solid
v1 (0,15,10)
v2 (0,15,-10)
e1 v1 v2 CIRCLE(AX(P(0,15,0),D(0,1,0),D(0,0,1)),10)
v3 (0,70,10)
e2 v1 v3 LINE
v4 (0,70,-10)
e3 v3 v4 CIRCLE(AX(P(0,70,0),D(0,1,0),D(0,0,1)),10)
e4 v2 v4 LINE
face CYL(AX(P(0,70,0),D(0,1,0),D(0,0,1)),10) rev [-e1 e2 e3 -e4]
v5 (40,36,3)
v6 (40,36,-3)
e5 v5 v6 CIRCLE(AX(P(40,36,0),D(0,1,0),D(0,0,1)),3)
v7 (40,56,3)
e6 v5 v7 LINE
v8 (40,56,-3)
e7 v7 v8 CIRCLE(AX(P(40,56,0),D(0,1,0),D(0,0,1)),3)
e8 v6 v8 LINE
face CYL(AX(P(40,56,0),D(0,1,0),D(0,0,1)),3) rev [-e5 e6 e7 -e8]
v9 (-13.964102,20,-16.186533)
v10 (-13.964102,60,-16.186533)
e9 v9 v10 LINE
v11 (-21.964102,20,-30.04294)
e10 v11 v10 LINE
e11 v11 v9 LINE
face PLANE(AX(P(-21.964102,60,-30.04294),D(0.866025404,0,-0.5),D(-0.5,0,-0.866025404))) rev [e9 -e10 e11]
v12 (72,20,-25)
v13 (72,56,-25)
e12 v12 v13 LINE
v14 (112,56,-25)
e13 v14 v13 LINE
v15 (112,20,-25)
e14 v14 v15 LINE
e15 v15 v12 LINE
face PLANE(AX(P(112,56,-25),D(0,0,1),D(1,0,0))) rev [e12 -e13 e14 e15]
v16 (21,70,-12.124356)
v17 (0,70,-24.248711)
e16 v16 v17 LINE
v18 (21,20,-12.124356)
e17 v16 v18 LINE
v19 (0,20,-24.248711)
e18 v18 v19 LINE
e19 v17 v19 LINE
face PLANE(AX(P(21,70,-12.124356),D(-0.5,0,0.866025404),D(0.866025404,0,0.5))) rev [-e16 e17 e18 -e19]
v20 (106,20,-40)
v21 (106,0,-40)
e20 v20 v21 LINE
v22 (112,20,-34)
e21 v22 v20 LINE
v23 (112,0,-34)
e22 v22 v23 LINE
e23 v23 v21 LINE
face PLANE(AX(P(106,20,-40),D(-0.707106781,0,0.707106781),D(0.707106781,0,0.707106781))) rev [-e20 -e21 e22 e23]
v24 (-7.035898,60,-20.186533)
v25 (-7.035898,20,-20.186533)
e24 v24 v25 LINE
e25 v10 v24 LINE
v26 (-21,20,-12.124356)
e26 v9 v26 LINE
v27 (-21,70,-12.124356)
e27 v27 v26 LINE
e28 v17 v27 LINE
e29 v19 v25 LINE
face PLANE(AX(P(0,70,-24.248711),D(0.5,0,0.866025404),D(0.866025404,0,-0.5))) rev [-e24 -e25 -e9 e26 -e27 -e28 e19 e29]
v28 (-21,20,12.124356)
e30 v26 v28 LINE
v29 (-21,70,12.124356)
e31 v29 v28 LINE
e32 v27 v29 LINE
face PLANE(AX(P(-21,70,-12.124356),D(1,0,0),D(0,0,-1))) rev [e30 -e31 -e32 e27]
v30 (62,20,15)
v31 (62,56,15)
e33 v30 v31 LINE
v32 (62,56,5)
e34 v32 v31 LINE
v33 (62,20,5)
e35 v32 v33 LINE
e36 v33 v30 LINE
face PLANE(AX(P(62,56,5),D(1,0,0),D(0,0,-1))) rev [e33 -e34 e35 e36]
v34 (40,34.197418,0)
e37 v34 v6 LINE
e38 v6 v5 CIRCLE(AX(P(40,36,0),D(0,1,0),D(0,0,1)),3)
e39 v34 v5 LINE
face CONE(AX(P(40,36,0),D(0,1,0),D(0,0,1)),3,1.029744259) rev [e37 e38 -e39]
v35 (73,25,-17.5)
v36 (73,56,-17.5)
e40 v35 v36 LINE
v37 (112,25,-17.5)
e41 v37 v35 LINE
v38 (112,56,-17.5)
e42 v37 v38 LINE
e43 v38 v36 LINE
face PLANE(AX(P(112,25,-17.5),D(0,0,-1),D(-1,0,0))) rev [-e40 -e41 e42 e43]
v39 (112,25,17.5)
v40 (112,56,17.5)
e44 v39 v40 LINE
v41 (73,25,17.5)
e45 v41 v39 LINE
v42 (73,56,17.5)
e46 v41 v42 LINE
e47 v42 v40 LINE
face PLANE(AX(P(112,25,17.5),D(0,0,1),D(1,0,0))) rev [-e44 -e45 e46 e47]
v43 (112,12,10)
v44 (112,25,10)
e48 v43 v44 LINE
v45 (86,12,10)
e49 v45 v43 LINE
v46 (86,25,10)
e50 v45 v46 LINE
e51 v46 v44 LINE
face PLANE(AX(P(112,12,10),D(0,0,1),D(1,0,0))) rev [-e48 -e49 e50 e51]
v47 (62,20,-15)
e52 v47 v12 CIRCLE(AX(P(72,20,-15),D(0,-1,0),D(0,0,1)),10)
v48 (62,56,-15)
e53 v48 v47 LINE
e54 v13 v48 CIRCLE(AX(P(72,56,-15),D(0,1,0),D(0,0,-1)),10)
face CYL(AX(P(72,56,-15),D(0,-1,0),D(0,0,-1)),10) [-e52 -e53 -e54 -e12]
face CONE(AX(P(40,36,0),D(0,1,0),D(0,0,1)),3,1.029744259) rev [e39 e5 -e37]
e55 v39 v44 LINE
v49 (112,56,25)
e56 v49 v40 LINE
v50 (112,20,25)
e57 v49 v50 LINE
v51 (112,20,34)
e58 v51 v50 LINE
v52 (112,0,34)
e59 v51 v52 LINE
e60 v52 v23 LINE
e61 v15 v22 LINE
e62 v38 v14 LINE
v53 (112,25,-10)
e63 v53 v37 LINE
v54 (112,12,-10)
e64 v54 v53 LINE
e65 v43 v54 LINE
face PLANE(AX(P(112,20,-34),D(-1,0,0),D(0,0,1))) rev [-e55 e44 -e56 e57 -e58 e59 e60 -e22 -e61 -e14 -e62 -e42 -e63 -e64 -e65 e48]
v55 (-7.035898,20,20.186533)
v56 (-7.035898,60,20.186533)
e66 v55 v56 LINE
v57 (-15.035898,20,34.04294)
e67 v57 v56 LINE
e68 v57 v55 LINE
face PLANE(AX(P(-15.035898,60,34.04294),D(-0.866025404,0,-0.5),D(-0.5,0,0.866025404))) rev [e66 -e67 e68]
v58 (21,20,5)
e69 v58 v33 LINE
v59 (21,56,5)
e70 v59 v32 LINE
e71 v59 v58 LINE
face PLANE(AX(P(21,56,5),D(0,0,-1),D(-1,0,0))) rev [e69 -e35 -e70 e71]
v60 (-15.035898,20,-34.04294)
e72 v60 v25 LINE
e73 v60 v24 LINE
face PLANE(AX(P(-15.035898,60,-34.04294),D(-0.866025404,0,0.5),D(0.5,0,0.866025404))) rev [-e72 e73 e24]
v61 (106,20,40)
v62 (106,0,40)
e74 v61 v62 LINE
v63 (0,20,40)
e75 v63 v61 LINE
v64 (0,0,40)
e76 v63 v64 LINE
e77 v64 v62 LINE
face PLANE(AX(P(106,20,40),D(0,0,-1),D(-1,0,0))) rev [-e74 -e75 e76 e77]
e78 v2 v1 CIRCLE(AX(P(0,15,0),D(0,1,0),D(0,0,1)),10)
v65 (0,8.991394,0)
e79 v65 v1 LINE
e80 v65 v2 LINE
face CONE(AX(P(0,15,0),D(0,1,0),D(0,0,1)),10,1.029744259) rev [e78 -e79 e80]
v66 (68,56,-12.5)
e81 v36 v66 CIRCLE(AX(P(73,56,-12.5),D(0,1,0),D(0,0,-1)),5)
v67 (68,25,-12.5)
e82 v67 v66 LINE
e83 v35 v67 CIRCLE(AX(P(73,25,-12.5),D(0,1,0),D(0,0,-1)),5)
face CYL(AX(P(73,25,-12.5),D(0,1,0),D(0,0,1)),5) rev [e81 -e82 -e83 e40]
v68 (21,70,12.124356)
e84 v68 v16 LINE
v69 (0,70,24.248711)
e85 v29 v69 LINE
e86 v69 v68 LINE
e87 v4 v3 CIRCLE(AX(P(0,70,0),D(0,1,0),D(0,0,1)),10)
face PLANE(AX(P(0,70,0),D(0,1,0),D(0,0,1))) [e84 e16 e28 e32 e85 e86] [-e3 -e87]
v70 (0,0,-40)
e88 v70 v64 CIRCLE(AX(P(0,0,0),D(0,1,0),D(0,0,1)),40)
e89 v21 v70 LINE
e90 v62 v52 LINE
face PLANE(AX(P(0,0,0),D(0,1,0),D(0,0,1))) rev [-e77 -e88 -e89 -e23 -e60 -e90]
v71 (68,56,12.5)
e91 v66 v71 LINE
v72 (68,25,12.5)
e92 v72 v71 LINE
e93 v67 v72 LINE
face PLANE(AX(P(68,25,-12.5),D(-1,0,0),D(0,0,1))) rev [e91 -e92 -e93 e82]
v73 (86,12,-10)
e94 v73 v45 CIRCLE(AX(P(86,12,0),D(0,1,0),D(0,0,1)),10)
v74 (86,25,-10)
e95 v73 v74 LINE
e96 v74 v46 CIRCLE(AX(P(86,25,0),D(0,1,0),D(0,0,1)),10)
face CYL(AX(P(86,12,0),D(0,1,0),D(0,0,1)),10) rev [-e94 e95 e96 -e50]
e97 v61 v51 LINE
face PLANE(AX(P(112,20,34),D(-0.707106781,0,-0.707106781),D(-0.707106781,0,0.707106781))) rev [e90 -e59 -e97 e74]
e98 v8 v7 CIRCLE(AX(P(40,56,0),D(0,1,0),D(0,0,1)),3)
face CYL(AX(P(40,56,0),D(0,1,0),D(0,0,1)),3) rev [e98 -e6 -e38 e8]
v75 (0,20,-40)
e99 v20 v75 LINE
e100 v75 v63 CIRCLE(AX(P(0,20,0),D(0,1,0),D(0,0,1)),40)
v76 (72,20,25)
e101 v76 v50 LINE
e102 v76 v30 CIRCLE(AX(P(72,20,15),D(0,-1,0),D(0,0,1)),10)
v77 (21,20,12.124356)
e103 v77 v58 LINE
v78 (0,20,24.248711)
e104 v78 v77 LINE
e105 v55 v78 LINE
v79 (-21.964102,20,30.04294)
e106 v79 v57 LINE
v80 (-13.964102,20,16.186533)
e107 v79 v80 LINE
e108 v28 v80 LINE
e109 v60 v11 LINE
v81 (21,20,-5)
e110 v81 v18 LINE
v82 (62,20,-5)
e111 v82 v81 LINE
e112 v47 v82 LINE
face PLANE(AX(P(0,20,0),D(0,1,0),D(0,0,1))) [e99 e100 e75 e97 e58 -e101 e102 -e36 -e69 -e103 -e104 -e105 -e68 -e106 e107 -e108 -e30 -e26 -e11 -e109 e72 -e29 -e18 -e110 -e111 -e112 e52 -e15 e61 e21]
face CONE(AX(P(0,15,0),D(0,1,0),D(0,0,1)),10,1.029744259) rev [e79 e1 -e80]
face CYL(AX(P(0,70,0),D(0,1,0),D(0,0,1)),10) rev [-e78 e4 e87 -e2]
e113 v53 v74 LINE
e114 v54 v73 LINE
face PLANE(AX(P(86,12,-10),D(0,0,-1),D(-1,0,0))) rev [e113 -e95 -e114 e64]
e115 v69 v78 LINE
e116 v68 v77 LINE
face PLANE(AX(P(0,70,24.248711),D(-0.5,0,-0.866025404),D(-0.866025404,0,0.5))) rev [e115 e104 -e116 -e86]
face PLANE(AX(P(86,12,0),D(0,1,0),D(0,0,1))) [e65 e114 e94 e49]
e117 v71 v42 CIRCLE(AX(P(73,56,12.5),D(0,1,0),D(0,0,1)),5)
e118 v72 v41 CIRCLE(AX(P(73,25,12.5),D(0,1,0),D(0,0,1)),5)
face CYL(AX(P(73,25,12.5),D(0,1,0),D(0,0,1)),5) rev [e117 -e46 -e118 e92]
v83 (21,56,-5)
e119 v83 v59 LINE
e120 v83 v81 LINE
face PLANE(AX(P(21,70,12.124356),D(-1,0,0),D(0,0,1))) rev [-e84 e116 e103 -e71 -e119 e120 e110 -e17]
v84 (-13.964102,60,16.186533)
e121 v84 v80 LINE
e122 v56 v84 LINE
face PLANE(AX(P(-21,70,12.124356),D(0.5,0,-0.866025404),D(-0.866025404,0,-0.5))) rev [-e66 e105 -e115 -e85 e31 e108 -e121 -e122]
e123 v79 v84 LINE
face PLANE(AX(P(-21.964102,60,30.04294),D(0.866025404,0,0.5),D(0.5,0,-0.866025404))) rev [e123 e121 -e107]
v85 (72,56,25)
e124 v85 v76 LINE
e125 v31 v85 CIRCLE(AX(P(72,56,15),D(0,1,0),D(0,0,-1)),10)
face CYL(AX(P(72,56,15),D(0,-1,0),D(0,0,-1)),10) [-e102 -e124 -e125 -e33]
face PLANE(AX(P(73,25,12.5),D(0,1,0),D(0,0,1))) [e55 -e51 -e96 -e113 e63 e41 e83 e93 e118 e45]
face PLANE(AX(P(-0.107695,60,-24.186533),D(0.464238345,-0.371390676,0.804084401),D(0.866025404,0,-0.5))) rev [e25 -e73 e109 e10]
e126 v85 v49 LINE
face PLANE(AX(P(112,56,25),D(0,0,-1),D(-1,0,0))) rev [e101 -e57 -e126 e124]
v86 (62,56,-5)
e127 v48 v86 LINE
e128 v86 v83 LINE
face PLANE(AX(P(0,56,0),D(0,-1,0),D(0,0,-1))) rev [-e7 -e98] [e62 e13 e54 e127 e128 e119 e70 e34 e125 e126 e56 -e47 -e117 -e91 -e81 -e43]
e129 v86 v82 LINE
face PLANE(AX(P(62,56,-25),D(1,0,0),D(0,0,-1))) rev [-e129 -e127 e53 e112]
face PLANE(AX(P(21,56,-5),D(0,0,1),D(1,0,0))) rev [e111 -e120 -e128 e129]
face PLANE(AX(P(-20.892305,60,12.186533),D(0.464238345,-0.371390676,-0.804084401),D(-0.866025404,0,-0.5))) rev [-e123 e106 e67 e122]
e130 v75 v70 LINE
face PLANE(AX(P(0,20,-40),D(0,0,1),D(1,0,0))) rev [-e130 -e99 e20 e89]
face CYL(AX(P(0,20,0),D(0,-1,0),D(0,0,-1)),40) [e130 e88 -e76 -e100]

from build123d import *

# Parameters (mm, degrees)
BASE_PLATE_DEPTH        = 20
HEX_MOUNTING_BOSS_DEPTH = 50
GUSSET_RIB_1_SKETCH_W   = 8
GUSSET_RIB_1_SKETCH_H   = 40
GUSSET_RIB_1_DEPTH      = 16
RIB_1_TRIM_CUT_DEPTH    = 16
GUSSET_RIB_2_SKETCH_W   = 8
GUSSET_RIB_2_SKETCH_H   = 40
GUSSET_RIB_2_DEPTH      = 16
RIB_2_TRIM_CUT_DEPTH    = 16
BOSS_BORE_20_D          = 20
BOSS_BORE_20_DEPTH      = 55
BOSS_BORE_20_TIP        = 6.00860619
SHAFT_HOUSING_DEPTH     = 36
HOUSING_FILLET_R10_R    = 10
HOUSING_POCKET_DEPTH    = 31
HOUSING_SLOT_DEPTH      = 13
CROSS_HOLE_6_D          = 6
CROSS_HOLE_6_DEPTH      = 20
CROSS_HOLE_6_TIP        = 1.802581857


with BuildPart() as part:
    # Base Plate Sketch → Base Plate (new body)
    with BuildSketch(Plane(origin=(0, 0, 0), x_dir=(1, 0, 0), z_dir=(0, 1, 0))):
        with BuildLine():
            Line((0, 40), (106, 40))
            Line((106, 40), (112, 34))
            Line((112, 34), (112, -34))
            Line((112, -34), (106, -40))
            Line((106, -40), (0, -40))
            ThreePointArc((0, -40), (-40, 0), (0, 40))
        make_face()
    extrude(amount=BASE_PLATE_DEPTH)

    # Hex Boss Sketch → Hex Mounting Boss (add)
    with BuildSketch(Plane(origin=(0, 20, 0), x_dir=(1, 0, 0), z_dir=(0, 1, 0))):
        Polygon((0, 24.248711306), (-21, 12.124355653), (-21, -12.124355653), (0, -24.248711306), (21, -12.124355653), (21, 12.124355653), align=None)
    extrude(amount=HEX_MOUNTING_BOSS_DEPTH)

    # Gusset Rib 1 Sketch → Gusset Rib 1 (add)
    with BuildSketch(Plane(origin=(-10.5, 0, 18.186533479), x_dir=(0.8660254037844417, 0, 0.4999999999999949), z_dir=(-0.4999999999999949, 0, 0.8660254037844417))):
        with Locations((0, 40)):
            Rectangle(GUSSET_RIB_1_SKETCH_W, GUSSET_RIB_1_SKETCH_H)
    extrude(amount=GUSSET_RIB_1_DEPTH)

    # Rib 1 Trim Sketch → Rib 1 Trim Cut (cut)
    with BuildSketch(Plane(origin=(3.464101615, 0, 2), x_dir=(0.49999999999999495, 0, -0.8660254037844417), z_dir=(0.8660254037844417, 0, 0.49999999999999495))):
        Polygon((-21, 60), (-37, 20), (-37, 60), align=None)
    extrude(amount=-RIB_1_TRIM_CUT_DEPTH, mode=Mode.SUBTRACT)

    # Gusset Rib 2 Sketch → Gusset Rib 2 (add)
    with BuildSketch(Plane(origin=(-10.5, 0, -18.186533479), x_dir=(-0.8660254037844386, 0, 0.4999999999999999), z_dir=(-0.49999999999999994, 0, -0.8660254037844387))):
        with Locations((0, 40)):
            Rectangle(GUSSET_RIB_2_SKETCH_W, GUSSET_RIB_2_SKETCH_H)
    extrude(amount=GUSSET_RIB_2_DEPTH)

    # Rib 2 Trim Sketch → Rib 2 Trim Cut (cut)
    with BuildSketch(Plane(origin=(-3.464101615, 0, 2), x_dir=(0.5000000000000001, 0, 0.8660254037844386), z_dir=(-0.8660254037844386, 0, 0.5000000000000001))):
        Polygon((-21, 60), (-37, 20), (-37, 60), align=None)
    extrude(amount=-RIB_2_TRIM_CUT_DEPTH, mode=Mode.SUBTRACT)

    # Boss Bore Ø20
    with Locations(Plane(origin=(0, 70, 0), x_dir=(1, 0, 0), z_dir=(0, 1, 0))):
        with Locations((0, 0)):
            Hole(BOSS_BORE_20_D / 2, depth=BOSS_BORE_20_DEPTH)
            with Locations((0, 0, -(BOSS_BORE_20_DEPTH + BOSS_BORE_20_TIP / 2))):  # 118° drill point
                Cone(0, BOSS_BORE_20_D / 2, BOSS_BORE_20_TIP, mode=Mode.SUBTRACT)

    # Shaft Housing Sketch → Shaft Housing (add)
    with BuildSketch(Plane(origin=(0, 20, 0), x_dir=(1, 0, 0), z_dir=(0, 1, 0))):
        Polygon((112, 25), (62, 25), (62, 5), (21, 5), (21, -5), (62, -5), (62, -25), (112, -25), align=None)
    extrude(amount=SHAFT_HOUSING_DEPTH)

    # Housing Fillet R10
    housing_fillet_r10_edges = [part.edges().sort_by_distance(p)[0] for p in [
        (62, 38, -25),
        (62, 38, 25),
    ]]
    fillet(housing_fillet_r10_edges, radius=HOUSING_FILLET_R10_R)

    # Housing Pocket Sketch → Housing Pocket (cut)
    with BuildSketch(Plane(origin=(0, 56, 0), x_dir=(1, 0, 0), z_dir=(0, 1, 0))):
        with BuildLine():
            Line((112, 17.5), (73, 17.5))
            ThreePointArc((73, 17.5), (69.464466094, 16.035533906), (68, 12.5))
            Line((68, 12.5), (68, -12.5))
            ThreePointArc((68, -12.5), (69.464466094, -16.035533906), (73, -17.5))
            Line((73, -17.5), (112, -17.5))
            Line((112, -17.5), (112, 17.5))
        make_face()
    extrude(amount=-HOUSING_POCKET_DEPTH, mode=Mode.SUBTRACT)

    # Housing Slot Sketch → Housing Slot (cut)
    with BuildSketch(Plane(origin=(0, 25, 0), x_dir=(1, 0, 0), z_dir=(0, 1, 0))):
        with BuildLine():
            Line((86, 10), (112, 10))
            Line((112, 10), (112, -10))
            Line((112, -10), (86, -10))
            ThreePointArc((86, -10), (76, 0), (86, 10))
        make_face()
    extrude(amount=-HOUSING_SLOT_DEPTH, mode=Mode.SUBTRACT)

    # Cross Hole Ø6
    with Locations(Plane(origin=(0, 56, 0), x_dir=(1, 0, 0), z_dir=(0, 1, 0))):
        with Locations((40, 0)):
            Hole(CROSS_HOLE_6_D / 2, depth=CROSS_HOLE_6_DEPTH)
            with Locations((0, 0, -(CROSS_HOLE_6_DEPTH + CROSS_HOLE_6_TIP / 2))):  # 118° drill point
                Cone(0, CROSS_HOLE_6_D / 2, CROSS_HOLE_6_TIP, mode=Mode.SUBTRACT)


solid = part.part
